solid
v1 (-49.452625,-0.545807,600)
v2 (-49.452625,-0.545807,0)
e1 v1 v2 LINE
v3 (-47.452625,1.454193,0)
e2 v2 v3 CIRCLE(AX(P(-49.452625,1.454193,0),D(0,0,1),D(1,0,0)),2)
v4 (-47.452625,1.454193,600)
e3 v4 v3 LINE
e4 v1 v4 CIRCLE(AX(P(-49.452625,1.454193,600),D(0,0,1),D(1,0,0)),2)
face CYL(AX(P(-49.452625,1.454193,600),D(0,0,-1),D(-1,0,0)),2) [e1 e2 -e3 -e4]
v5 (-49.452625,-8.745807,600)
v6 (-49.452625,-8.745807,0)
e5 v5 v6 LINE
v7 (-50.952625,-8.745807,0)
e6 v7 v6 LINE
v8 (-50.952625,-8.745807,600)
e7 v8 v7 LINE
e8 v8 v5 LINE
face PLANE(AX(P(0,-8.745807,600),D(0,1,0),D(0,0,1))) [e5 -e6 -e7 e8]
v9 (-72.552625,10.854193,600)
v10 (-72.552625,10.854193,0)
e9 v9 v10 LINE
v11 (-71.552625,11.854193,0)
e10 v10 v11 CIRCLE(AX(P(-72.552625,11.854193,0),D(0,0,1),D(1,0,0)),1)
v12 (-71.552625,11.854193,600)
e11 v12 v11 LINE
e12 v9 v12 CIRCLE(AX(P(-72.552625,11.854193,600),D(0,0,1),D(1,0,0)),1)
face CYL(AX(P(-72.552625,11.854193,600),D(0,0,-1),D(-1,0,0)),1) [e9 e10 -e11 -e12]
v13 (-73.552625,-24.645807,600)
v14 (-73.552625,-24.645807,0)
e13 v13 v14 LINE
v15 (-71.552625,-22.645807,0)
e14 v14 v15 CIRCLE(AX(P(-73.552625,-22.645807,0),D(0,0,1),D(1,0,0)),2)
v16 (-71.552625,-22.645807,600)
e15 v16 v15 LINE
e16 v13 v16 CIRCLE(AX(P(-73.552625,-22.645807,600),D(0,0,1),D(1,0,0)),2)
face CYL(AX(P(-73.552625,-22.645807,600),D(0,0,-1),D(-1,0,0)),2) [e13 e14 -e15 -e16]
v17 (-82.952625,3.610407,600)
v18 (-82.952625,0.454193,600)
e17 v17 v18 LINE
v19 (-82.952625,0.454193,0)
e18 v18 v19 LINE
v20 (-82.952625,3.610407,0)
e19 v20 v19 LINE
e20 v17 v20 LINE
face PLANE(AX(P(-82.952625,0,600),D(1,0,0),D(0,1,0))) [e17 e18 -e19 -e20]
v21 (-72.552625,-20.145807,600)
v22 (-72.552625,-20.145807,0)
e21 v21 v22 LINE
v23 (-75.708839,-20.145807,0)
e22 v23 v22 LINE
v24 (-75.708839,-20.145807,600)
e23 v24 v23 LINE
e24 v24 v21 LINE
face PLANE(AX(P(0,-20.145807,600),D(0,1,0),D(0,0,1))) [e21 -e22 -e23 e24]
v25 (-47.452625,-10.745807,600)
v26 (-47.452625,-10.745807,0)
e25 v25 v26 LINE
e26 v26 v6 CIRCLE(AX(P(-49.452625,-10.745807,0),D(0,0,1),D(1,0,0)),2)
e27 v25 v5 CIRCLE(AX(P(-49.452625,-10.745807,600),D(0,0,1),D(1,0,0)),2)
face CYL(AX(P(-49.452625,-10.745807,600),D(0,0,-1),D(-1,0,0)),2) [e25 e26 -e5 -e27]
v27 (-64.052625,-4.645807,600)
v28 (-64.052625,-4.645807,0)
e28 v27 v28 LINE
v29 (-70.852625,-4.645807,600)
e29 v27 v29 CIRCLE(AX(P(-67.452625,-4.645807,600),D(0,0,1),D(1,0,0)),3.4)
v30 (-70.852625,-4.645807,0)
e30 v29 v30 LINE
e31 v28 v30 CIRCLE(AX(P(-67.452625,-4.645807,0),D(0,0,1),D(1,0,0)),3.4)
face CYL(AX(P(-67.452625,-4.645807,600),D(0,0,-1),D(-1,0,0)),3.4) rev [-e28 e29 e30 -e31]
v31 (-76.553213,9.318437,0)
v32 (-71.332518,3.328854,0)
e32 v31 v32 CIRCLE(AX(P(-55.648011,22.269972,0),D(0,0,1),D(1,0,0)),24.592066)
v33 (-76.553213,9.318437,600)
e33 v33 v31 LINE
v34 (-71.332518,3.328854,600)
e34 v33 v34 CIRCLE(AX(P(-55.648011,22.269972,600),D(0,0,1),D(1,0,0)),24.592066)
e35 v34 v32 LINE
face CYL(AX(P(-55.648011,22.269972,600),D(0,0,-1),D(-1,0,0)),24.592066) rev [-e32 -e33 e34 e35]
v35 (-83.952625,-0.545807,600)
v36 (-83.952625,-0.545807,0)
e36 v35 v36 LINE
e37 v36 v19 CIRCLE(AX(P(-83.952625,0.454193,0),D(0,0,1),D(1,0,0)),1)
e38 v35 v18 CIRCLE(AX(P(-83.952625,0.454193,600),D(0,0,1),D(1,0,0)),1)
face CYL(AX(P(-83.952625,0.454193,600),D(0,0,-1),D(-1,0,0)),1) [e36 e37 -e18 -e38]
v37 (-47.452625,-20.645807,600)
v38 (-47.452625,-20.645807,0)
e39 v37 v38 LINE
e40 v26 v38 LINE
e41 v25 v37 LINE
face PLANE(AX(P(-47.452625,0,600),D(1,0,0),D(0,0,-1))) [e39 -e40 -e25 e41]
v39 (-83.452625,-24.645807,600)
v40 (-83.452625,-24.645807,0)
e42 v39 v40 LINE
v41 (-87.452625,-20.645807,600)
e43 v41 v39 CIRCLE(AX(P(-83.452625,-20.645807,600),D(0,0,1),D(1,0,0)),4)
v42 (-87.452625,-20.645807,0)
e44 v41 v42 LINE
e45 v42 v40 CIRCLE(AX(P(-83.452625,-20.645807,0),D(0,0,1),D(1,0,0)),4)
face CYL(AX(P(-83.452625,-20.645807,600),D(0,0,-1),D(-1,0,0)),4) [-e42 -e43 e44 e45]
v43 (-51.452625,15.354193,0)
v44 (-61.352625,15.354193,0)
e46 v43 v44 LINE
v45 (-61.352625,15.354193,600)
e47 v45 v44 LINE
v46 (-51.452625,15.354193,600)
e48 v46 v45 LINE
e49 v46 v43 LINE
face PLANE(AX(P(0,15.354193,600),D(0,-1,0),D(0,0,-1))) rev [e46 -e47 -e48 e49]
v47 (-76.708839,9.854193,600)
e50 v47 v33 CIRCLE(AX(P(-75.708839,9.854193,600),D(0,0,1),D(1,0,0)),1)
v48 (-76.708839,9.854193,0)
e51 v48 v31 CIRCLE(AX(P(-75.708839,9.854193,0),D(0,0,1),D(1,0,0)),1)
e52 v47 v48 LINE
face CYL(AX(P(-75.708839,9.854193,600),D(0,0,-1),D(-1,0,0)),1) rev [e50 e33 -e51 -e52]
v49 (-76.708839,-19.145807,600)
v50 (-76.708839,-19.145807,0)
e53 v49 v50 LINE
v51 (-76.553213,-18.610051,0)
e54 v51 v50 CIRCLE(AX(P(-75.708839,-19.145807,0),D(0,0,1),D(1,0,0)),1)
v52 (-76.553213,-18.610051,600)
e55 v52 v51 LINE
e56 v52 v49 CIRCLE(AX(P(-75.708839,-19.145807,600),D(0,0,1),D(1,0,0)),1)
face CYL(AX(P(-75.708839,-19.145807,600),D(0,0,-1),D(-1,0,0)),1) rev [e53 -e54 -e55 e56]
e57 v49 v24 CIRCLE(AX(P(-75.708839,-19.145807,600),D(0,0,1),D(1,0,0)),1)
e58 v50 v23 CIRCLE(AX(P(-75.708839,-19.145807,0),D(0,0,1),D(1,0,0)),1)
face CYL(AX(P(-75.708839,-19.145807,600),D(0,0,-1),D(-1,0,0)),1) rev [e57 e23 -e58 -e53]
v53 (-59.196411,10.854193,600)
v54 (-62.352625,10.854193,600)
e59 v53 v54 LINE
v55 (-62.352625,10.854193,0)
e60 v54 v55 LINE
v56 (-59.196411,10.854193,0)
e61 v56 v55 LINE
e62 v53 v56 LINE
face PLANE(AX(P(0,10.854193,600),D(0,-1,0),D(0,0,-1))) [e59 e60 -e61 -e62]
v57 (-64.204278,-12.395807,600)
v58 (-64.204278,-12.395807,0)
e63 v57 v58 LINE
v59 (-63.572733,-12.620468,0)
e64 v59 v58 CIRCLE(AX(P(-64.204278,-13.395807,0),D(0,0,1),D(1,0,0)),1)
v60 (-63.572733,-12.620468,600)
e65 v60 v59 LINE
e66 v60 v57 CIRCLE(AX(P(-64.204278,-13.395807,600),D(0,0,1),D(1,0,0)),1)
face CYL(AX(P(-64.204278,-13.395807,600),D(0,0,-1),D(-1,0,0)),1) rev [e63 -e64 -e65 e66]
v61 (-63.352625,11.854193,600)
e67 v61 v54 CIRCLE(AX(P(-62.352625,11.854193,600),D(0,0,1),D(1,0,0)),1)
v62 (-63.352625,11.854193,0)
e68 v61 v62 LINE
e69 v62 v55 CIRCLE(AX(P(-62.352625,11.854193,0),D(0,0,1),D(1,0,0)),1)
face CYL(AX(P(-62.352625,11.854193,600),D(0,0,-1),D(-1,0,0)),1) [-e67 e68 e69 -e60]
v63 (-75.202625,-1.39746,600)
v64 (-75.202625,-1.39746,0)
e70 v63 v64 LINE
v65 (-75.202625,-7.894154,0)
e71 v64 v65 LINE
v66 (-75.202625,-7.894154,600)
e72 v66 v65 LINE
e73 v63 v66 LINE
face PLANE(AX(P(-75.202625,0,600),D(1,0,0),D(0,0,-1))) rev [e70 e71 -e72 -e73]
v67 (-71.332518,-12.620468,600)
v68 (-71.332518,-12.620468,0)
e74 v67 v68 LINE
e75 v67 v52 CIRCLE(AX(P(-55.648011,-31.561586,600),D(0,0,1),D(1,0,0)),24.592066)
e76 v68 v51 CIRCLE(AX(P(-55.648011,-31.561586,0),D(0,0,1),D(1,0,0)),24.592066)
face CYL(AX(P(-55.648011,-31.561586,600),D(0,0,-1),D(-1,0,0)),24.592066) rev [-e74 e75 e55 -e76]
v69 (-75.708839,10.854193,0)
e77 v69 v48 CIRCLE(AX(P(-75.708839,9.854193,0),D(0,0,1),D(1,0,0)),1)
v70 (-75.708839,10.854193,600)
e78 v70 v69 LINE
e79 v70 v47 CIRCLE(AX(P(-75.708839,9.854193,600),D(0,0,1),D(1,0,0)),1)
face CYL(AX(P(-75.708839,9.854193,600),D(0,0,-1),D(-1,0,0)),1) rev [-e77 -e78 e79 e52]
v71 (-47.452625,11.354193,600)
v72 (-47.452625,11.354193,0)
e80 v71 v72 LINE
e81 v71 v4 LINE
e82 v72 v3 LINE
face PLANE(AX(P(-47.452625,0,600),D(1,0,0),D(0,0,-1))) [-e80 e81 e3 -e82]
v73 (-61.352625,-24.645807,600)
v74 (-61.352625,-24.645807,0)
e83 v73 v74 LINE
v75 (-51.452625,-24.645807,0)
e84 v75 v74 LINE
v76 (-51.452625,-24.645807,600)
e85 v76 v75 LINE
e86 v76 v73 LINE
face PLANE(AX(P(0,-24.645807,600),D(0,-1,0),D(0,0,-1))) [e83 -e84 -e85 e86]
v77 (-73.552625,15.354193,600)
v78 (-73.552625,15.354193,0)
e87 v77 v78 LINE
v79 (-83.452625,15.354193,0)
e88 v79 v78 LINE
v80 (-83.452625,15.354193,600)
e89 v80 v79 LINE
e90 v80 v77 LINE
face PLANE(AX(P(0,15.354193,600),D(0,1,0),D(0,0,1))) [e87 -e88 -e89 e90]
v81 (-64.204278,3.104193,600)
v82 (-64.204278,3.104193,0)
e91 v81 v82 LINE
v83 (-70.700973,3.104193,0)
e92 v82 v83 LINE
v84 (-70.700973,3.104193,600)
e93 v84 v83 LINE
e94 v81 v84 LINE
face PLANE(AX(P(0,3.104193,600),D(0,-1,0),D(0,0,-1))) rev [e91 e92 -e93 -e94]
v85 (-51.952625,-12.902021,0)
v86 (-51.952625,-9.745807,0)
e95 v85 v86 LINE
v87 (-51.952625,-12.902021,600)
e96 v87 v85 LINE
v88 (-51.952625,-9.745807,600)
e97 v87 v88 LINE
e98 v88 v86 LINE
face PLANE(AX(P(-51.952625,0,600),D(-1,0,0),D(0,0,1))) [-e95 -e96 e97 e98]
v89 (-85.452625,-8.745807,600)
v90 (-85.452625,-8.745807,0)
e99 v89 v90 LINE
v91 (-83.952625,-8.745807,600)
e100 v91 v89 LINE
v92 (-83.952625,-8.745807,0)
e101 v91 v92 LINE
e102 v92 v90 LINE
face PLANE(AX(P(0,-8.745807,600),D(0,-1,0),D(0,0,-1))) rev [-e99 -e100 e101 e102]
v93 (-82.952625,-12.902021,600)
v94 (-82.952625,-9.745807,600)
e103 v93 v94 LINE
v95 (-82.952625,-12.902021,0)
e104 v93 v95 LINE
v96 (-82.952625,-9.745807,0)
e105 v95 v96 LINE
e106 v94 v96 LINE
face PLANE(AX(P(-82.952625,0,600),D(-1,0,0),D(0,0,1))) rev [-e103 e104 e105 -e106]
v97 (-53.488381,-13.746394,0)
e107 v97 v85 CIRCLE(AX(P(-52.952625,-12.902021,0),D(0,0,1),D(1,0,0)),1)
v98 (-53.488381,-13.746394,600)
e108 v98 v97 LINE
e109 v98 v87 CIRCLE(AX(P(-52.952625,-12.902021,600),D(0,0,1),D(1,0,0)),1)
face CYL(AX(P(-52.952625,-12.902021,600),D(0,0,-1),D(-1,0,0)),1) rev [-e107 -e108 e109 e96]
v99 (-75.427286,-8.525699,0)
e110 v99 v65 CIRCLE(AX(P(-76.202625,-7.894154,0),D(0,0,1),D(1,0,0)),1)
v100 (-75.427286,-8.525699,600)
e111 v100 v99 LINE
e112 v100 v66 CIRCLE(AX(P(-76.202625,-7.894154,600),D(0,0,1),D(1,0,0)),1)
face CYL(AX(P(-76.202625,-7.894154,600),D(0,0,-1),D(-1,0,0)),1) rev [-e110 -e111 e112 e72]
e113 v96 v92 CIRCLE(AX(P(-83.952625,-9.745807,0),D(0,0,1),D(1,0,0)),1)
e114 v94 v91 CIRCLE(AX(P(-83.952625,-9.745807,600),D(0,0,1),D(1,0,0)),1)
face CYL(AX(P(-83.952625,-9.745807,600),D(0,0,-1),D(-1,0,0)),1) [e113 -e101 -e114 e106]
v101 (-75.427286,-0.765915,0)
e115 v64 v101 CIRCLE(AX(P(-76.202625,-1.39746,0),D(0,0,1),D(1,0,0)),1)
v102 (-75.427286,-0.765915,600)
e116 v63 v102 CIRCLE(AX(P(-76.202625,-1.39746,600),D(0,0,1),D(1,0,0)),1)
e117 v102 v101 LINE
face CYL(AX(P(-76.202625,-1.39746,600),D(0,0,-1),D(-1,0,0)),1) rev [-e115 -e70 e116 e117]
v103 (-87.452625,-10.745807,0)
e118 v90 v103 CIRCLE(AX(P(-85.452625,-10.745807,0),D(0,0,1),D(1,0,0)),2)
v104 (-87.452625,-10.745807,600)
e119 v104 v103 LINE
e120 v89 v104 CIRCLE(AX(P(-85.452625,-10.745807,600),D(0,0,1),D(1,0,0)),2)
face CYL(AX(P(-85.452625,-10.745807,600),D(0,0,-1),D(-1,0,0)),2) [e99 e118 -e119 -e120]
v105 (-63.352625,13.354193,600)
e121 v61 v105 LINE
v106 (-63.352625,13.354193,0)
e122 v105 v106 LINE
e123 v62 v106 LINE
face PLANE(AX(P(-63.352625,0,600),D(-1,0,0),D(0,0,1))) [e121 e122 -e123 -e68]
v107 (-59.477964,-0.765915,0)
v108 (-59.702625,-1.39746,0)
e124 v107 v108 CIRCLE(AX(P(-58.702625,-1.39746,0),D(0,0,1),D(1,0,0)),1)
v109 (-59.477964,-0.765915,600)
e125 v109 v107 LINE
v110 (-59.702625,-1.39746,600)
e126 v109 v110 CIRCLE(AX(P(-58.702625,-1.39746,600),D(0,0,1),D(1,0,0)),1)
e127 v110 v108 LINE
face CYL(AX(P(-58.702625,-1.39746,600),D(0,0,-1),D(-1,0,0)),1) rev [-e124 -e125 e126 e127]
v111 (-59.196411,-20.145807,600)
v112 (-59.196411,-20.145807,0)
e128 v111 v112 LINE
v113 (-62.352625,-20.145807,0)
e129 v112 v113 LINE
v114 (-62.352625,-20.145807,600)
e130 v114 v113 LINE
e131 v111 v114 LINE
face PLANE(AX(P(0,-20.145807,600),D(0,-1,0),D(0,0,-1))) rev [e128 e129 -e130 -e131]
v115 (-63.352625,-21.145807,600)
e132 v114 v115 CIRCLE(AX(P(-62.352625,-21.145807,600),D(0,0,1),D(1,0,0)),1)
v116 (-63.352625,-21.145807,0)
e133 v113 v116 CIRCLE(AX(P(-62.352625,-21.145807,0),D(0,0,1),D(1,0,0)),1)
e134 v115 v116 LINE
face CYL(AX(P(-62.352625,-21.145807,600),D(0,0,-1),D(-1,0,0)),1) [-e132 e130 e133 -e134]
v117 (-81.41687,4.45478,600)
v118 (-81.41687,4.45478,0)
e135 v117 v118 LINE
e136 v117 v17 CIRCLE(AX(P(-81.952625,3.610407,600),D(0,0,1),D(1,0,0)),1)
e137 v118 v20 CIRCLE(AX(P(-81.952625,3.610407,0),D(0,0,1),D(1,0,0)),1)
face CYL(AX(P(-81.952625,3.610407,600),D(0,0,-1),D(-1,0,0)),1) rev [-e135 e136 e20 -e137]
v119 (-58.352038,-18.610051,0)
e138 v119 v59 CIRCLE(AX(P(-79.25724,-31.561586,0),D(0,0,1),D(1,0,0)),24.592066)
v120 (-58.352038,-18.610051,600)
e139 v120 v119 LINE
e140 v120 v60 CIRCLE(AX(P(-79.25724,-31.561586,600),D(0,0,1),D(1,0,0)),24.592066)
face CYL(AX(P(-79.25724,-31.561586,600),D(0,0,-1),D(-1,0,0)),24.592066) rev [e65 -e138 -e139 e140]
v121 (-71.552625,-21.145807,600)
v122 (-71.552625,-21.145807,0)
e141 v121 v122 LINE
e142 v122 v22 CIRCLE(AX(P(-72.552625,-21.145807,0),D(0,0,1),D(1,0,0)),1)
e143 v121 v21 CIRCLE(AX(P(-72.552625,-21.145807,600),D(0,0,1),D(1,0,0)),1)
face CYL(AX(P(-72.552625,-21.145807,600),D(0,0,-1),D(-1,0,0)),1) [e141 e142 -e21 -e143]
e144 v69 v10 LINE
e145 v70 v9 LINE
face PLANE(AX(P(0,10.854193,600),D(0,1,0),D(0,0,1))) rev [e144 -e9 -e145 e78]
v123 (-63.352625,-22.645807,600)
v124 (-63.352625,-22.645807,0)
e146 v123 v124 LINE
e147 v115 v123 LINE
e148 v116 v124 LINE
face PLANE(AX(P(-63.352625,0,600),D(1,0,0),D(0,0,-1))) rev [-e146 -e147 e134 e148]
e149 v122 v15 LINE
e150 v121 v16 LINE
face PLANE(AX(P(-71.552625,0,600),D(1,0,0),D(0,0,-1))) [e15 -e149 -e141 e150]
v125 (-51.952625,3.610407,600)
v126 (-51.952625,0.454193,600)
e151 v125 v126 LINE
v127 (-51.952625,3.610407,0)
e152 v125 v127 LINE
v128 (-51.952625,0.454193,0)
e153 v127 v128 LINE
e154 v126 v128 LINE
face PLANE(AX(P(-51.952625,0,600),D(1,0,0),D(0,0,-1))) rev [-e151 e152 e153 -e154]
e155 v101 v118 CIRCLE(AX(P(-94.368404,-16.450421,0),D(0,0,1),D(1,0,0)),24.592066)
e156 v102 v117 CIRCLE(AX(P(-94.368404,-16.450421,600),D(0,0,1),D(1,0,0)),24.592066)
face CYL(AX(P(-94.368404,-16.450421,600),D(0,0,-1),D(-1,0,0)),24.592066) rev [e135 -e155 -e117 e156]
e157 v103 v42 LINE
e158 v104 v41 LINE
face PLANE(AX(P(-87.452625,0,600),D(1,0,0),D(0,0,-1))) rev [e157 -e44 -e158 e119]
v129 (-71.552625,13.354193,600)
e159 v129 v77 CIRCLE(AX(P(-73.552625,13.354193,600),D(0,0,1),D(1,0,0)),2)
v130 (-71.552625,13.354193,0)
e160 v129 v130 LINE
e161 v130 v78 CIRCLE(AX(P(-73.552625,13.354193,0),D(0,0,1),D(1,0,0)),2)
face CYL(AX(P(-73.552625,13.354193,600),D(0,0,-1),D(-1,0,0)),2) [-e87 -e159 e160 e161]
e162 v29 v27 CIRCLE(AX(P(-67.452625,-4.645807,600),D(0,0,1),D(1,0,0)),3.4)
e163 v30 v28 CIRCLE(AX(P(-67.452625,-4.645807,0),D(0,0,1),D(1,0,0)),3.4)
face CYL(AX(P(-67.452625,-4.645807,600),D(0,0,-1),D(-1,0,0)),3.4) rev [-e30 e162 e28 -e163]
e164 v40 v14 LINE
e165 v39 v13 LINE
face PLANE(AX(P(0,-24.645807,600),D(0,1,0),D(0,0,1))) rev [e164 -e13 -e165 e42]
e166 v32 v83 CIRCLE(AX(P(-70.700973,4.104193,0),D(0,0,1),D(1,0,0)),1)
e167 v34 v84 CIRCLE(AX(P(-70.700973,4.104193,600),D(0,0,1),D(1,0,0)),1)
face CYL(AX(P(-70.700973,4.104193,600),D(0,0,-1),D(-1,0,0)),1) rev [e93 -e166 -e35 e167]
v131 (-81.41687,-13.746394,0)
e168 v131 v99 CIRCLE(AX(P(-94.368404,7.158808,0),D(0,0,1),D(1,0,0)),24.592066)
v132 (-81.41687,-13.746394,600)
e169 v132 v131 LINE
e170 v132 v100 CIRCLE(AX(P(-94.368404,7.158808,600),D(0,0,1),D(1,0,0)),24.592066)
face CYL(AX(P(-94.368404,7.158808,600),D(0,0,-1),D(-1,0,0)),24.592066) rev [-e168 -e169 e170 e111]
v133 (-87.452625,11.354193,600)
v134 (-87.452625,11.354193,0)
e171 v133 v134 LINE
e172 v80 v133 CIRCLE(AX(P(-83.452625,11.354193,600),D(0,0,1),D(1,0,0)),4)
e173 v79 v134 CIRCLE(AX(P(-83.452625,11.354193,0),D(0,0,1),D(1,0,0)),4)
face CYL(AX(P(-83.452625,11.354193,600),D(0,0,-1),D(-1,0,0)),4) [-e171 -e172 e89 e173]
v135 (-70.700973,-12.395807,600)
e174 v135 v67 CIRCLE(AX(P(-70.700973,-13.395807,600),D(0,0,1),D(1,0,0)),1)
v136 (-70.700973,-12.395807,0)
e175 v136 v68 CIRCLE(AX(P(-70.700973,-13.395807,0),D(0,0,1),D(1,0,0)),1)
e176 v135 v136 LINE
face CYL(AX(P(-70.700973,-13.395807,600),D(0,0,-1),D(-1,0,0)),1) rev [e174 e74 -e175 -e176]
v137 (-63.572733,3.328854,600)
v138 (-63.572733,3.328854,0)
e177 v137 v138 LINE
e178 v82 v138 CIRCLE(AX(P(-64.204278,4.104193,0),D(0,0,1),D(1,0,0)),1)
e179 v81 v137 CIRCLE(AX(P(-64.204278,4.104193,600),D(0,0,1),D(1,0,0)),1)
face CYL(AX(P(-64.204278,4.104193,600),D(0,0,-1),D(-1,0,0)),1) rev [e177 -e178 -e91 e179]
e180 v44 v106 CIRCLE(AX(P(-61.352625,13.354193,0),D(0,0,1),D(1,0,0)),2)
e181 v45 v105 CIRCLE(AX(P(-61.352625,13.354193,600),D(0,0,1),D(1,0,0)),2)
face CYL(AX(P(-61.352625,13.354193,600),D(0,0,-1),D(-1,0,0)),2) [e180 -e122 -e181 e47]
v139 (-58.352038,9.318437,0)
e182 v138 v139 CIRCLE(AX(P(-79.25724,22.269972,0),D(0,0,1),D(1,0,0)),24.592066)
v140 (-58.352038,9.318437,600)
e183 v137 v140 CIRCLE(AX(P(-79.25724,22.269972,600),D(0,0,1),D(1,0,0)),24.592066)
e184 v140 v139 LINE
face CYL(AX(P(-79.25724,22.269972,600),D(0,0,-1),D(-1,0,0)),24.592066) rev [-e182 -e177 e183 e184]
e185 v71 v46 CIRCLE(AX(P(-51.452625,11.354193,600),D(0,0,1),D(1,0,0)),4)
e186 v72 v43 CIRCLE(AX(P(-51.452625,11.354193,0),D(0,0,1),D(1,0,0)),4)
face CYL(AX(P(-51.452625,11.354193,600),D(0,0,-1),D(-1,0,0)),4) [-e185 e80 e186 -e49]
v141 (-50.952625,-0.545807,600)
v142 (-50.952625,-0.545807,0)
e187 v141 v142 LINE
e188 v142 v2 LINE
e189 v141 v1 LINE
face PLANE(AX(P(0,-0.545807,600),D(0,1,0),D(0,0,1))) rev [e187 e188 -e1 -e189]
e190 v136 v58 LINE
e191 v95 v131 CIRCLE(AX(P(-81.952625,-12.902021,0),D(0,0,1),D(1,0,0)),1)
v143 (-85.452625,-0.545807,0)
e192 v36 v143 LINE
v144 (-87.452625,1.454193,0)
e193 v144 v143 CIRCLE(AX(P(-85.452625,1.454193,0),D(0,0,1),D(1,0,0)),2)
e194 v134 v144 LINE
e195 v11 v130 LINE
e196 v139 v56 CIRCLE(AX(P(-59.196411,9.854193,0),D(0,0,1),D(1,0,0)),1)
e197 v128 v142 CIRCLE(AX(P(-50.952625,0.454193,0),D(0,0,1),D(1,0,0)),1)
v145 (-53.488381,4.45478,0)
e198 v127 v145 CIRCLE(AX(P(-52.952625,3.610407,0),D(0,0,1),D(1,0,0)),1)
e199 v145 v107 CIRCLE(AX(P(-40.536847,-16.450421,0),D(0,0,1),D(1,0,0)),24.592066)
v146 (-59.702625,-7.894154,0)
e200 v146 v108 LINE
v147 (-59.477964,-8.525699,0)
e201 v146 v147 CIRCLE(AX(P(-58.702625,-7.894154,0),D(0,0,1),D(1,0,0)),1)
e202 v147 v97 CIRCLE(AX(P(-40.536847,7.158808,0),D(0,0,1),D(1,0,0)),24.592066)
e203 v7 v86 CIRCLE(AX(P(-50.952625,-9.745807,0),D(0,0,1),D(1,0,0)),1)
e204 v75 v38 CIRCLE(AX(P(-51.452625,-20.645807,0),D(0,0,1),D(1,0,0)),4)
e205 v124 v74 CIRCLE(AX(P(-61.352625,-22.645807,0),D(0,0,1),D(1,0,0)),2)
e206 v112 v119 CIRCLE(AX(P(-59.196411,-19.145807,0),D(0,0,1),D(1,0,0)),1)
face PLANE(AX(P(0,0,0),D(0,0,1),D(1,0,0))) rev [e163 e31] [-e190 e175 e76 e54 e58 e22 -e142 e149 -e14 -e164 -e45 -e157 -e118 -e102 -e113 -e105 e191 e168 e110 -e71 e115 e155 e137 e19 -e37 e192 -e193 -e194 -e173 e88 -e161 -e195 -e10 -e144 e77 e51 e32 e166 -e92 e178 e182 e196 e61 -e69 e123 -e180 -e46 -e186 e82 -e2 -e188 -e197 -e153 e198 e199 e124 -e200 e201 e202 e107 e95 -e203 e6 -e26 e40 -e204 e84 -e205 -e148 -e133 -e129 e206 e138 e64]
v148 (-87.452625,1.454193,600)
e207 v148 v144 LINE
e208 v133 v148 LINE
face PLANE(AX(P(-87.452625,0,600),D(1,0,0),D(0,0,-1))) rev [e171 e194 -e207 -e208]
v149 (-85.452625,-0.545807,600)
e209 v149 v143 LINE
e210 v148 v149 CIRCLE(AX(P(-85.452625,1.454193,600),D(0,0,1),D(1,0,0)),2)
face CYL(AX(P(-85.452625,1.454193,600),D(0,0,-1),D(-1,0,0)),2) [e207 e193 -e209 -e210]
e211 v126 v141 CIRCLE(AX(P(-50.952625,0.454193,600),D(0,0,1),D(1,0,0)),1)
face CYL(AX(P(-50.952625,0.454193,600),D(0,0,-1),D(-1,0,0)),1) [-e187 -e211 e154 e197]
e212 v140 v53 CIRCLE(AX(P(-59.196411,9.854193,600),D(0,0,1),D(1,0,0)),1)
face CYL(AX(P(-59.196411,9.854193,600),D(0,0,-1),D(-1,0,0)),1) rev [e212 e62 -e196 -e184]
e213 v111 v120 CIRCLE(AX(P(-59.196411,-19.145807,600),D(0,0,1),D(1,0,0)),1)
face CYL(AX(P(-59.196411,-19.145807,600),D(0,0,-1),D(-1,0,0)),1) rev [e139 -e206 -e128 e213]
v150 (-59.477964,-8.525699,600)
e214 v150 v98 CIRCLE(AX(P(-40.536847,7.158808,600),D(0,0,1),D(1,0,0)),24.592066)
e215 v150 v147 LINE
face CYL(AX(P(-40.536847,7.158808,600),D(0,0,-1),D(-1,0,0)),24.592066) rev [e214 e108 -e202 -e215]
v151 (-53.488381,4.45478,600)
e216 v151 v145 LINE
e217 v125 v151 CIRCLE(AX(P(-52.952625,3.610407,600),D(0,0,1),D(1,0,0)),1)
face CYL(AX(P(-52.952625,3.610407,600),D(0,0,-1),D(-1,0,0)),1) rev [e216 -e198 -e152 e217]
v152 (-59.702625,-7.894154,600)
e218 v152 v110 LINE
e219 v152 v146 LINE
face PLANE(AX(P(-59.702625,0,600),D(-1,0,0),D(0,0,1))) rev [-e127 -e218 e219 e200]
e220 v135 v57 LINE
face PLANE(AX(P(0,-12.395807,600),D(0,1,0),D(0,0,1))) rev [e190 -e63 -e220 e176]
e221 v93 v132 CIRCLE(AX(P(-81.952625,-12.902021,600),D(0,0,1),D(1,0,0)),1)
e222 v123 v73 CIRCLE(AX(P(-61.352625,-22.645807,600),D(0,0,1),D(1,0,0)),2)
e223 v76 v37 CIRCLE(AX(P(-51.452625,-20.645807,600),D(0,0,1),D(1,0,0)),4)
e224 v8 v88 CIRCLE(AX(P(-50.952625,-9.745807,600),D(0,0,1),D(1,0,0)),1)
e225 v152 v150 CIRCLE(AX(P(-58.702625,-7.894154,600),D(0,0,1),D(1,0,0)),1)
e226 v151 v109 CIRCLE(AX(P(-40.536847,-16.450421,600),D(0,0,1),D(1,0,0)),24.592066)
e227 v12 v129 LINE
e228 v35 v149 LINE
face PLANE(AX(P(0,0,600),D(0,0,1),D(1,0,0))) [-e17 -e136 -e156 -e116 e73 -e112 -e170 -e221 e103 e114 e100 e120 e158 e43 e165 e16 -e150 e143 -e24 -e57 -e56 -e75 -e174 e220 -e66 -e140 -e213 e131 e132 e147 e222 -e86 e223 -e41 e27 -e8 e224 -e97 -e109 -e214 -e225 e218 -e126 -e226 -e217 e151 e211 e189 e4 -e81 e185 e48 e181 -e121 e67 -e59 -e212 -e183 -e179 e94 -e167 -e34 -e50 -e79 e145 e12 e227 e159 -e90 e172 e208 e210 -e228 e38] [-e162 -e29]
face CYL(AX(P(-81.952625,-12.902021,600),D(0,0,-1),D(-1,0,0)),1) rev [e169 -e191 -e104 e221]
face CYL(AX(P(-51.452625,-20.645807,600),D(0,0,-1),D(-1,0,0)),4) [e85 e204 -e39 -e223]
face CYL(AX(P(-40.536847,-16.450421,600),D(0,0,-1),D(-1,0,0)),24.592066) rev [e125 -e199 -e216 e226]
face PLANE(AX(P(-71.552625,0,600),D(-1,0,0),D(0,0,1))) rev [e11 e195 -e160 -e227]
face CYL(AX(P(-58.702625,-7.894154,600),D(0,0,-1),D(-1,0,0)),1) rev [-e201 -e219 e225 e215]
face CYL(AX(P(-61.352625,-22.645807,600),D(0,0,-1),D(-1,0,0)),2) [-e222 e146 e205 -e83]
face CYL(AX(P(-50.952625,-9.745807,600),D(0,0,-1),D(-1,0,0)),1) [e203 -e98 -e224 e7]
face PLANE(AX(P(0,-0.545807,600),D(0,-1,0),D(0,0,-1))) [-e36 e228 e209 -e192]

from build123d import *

# Parameters (mm, degrees)
SKETCH1_R           = 3.4
BOSS_EXTRUDE1_DEPTH = 600


with BuildPart() as part:
    # Sketch1 → Boss-Extrude1 (new body)
    with BuildSketch(Plane.XY):
        with BuildLine():
            Line((-72.552625451, -20.1458069), (-75.708839475, -20.1458069))
            ThreePointArc((-75.708839475, -20.1458069), (-76.585125865, -19.62759748), (-76.55321253, -18.610051226))
            ThreePointArc((-76.55321253, -18.610051226), (-74.186362214, -15.403020453), (-71.332517782, -12.620467892))
            ThreePointArc((-71.332517782, -12.620467892), (-71.036129936, -12.453644757), (-70.700972516, -12.3958069))
            Line((-70.700972516, -12.3958069), (-67.452625451, -12.3958069))
            Line((-67.452625451, -12.3958069), (-64.204278386, -12.3958069))
            ThreePointArc((-64.204278386, -12.3958069), (-63.869120967, -12.453644757), (-63.572733121, -12.620467892))
            ThreePointArc((-63.572733121, -12.620467892), (-60.718888688, -15.403020453), (-58.352038372, -18.610051226))
            ThreePointArc((-58.352038372, -18.610051226), (-58.320125037, -19.62759748), (-59.196411427, -20.1458069))
            Line((-59.196411427, -20.1458069), (-62.352625451, -20.1458069))
            ThreePointArc((-62.352625451, -20.1458069), (-63.059732232, -20.438700119), (-63.352625451, -21.1458069))
            Line((-63.352625451, -21.1458069), (-63.352625451, -22.6458069))
            ThreePointArc((-63.352625451, -22.6458069), (-62.766839013, -24.060020463), (-61.352625451, -24.6458069))
            Line((-61.352625451, -24.6458069), (-51.452625451, -24.6458069))
            ThreePointArc((-51.452625451, -24.6458069), (-48.624198326, -23.474234025), (-47.452625451, -20.6458069))
            Line((-47.452625451, -20.6458069), (-47.452625451, -10.7458069))
            ThreePointArc((-47.452625451, -10.7458069), (-48.038411889, -9.331593338), (-49.452625451, -8.7458069))
            Line((-49.452625451, -8.7458069), (-50.952625451, -8.7458069))
            ThreePointArc((-50.952625451, -8.7458069), (-51.659732232, -9.038700119), (-51.952625451, -9.7458069))
            Line((-51.952625451, -9.7458069), (-51.952625451, -12.902020924))
            ThreePointArc((-51.952625451, -12.902020924), (-52.470834871, -13.778307314), (-53.488381126, -13.74639398))
            ThreePointArc((-53.488381126, -13.74639398), (-56.695411898, -11.379543663), (-59.477964459, -8.525699231))
            ThreePointArc((-59.477964459, -8.525699231), (-59.644787594, -8.229311385), (-59.702625451, -7.894153965))
            Line((-59.702625451, -7.894153965), (-59.702625451, -4.6458069))
            Line((-59.702625451, -4.6458069), (-59.702625451, -1.397459836))
            ThreePointArc((-59.702625451, -1.397459836), (-59.644787594, -1.062302416), (-59.477964459, -0.76591457))
            ThreePointArc((-59.477964459, -0.76591457), (-56.695411898, 2.087929862), (-53.488381126, 4.454780179))
            ThreePointArc((-53.488381126, 4.454780179), (-52.470834871, 4.486693513), (-51.952625451, 3.610407123))
            Line((-51.952625451, 3.610407123), (-51.952625451, 0.4541931))
            ThreePointArc((-51.952625451, 0.4541931), (-51.659732232, -0.252913682), (-50.952625451, -0.5458069))
            Line((-50.952625451, -0.5458069), (-49.452625451, -0.5458069))
            ThreePointArc((-49.452625451, -0.5458069), (-48.038411889, 0.039979537), (-47.452625451, 1.4541931))
            Line((-47.452625451, 1.4541931), (-47.452625451, 11.3541931))
            ThreePointArc((-47.452625451, 11.3541931), (-48.624198326, 14.182620224), (-51.452625451, 15.3541931))
            Line((-51.452625451, 15.3541931), (-61.352625451, 15.3541931))
            ThreePointArc((-61.352625451, 15.3541931), (-62.766839013, 14.768406662), (-63.352625451, 13.3541931))
            Line((-63.352625451, 13.3541931), (-63.352625451, 11.8541931))
            ThreePointArc((-63.352625451, 11.8541931), (-63.059732232, 11.147086318), (-62.352625451, 10.8541931))
            Line((-62.352625451, 10.8541931), (-59.196411427, 10.8541931))
            ThreePointArc((-59.196411427, 10.8541931), (-58.320125037, 10.335983679), (-58.352038372, 9.318437425))
            ThreePointArc((-58.352038372, 9.318437425), (-60.718888688, 6.111406652), (-63.572733121, 3.328854091))
            ThreePointArc((-63.572733121, 3.328854091), (-63.869120967, 3.162030956), (-64.204278386, 3.1041931))
            Line((-64.204278386, 3.1041931), (-67.452625451, 3.1041931))
            Line((-67.452625451, 3.1041931), (-70.700972516, 3.1041931))
            ThreePointArc((-70.700972516, 3.1041931), (-71.036129936, 3.162030956), (-71.332517782, 3.328854091))
            ThreePointArc((-71.332517782, 3.328854091), (-74.186362214, 6.111406652), (-76.55321253, 9.318437425))
            ThreePointArc((-76.55321253, 9.318437425), (-76.585125865, 10.335983679), (-75.708839475, 10.8541931))
            Line((-75.708839475, 10.8541931), (-72.552625451, 10.8541931))
            ThreePointArc((-72.552625451, 10.8541931), (-71.84551867, 11.147086318), (-71.552625451, 11.8541931))
            Line((-71.552625451, 11.8541931), (-71.552625451, 13.3541931))
            ThreePointArc((-71.552625451, 13.3541931), (-72.138411889, 14.768406662), (-73.552625451, 15.3541931))
            Line((-73.552625451, 15.3541931), (-83.452625451, 15.3541931))
            ThreePointArc((-83.452625451, 15.3541931), (-86.281052576, 14.182620224), (-87.452625451, 11.3541931))
            Line((-87.452625451, 11.3541931), (-87.452625451, 1.4541931))
            ThreePointArc((-87.452625451, 1.4541931), (-86.866839013, 0.039979537), (-85.452625451, -0.5458069))
            Line((-85.452625451, -0.5458069), (-83.952625451, -0.5458069))
            ThreePointArc((-83.952625451, -0.5458069), (-83.24551867, -0.252913682), (-82.952625451, 0.4541931))
            Line((-82.952625451, 0.4541931), (-82.952625451, 3.610407123))
            ThreePointArc((-82.952625451, 3.610407123), (-82.434416031, 4.486693513), (-81.416869776, 4.454780179))
            ThreePointArc((-81.416869776, 4.454780179), (-78.209839004, 2.087929862), (-75.427286443, -0.76591457))
            ThreePointArc((-75.427286443, -0.76591457), (-75.260463308, -1.062302416), (-75.202625451, -1.397459836))
            Line((-75.202625451, -1.397459836), (-75.202625451, -4.6458069))
            Line((-75.202625451, -4.6458069), (-75.202625451, -7.894153965))
            ThreePointArc((-75.202625451, -7.894153965), (-75.260463308, -8.229311385), (-75.427286443, -8.525699231))
            ThreePointArc((-75.427286443, -8.525699231), (-78.209839004, -11.379543663), (-81.416869776, -13.74639398))
            ThreePointArc((-81.416869776, -13.74639398), (-82.434416031, -13.778307314), (-82.952625451, -12.902020924))
            Line((-82.952625451, -12.902020924), (-82.952625451, -9.7458069))
            ThreePointArc((-82.952625451, -9.7458069), (-83.24551867, -9.038700119), (-83.952625451, -8.7458069))
            Line((-83.952625451, -8.7458069), (-85.452625451, -8.7458069))
            ThreePointArc((-85.452625451, -8.7458069), (-86.866839013, -9.331593338), (-87.452625451, -10.7458069))
            Line((-87.452625451, -10.7458069), (-87.452625451, -20.6458069))
            ThreePointArc((-87.452625451, -20.6458069), (-86.281052576, -23.474234025), (-83.452625451, -24.6458069))
            Line((-83.452625451, -24.6458069), (-73.552625451, -24.6458069))
            ThreePointArc((-73.552625451, -24.6458069), (-72.138411889, -24.060020463), (-71.552625451, -22.6458069))
            Line((-71.552625451, -22.6458069), (-71.552625451, -21.1458069))
            ThreePointArc((-71.552625451, -21.1458069), (-71.84551867, -20.438700119), (-72.552625451, -20.1458069))
        make_face()
        with Locations((-67.452625451, -4.6458069)):
            Circle(SKETCH1_R, mode=Mode.SUBTRACT)
    extrude(amount=BOSS_EXTRUDE1_DEPTH)


solid = part.part
